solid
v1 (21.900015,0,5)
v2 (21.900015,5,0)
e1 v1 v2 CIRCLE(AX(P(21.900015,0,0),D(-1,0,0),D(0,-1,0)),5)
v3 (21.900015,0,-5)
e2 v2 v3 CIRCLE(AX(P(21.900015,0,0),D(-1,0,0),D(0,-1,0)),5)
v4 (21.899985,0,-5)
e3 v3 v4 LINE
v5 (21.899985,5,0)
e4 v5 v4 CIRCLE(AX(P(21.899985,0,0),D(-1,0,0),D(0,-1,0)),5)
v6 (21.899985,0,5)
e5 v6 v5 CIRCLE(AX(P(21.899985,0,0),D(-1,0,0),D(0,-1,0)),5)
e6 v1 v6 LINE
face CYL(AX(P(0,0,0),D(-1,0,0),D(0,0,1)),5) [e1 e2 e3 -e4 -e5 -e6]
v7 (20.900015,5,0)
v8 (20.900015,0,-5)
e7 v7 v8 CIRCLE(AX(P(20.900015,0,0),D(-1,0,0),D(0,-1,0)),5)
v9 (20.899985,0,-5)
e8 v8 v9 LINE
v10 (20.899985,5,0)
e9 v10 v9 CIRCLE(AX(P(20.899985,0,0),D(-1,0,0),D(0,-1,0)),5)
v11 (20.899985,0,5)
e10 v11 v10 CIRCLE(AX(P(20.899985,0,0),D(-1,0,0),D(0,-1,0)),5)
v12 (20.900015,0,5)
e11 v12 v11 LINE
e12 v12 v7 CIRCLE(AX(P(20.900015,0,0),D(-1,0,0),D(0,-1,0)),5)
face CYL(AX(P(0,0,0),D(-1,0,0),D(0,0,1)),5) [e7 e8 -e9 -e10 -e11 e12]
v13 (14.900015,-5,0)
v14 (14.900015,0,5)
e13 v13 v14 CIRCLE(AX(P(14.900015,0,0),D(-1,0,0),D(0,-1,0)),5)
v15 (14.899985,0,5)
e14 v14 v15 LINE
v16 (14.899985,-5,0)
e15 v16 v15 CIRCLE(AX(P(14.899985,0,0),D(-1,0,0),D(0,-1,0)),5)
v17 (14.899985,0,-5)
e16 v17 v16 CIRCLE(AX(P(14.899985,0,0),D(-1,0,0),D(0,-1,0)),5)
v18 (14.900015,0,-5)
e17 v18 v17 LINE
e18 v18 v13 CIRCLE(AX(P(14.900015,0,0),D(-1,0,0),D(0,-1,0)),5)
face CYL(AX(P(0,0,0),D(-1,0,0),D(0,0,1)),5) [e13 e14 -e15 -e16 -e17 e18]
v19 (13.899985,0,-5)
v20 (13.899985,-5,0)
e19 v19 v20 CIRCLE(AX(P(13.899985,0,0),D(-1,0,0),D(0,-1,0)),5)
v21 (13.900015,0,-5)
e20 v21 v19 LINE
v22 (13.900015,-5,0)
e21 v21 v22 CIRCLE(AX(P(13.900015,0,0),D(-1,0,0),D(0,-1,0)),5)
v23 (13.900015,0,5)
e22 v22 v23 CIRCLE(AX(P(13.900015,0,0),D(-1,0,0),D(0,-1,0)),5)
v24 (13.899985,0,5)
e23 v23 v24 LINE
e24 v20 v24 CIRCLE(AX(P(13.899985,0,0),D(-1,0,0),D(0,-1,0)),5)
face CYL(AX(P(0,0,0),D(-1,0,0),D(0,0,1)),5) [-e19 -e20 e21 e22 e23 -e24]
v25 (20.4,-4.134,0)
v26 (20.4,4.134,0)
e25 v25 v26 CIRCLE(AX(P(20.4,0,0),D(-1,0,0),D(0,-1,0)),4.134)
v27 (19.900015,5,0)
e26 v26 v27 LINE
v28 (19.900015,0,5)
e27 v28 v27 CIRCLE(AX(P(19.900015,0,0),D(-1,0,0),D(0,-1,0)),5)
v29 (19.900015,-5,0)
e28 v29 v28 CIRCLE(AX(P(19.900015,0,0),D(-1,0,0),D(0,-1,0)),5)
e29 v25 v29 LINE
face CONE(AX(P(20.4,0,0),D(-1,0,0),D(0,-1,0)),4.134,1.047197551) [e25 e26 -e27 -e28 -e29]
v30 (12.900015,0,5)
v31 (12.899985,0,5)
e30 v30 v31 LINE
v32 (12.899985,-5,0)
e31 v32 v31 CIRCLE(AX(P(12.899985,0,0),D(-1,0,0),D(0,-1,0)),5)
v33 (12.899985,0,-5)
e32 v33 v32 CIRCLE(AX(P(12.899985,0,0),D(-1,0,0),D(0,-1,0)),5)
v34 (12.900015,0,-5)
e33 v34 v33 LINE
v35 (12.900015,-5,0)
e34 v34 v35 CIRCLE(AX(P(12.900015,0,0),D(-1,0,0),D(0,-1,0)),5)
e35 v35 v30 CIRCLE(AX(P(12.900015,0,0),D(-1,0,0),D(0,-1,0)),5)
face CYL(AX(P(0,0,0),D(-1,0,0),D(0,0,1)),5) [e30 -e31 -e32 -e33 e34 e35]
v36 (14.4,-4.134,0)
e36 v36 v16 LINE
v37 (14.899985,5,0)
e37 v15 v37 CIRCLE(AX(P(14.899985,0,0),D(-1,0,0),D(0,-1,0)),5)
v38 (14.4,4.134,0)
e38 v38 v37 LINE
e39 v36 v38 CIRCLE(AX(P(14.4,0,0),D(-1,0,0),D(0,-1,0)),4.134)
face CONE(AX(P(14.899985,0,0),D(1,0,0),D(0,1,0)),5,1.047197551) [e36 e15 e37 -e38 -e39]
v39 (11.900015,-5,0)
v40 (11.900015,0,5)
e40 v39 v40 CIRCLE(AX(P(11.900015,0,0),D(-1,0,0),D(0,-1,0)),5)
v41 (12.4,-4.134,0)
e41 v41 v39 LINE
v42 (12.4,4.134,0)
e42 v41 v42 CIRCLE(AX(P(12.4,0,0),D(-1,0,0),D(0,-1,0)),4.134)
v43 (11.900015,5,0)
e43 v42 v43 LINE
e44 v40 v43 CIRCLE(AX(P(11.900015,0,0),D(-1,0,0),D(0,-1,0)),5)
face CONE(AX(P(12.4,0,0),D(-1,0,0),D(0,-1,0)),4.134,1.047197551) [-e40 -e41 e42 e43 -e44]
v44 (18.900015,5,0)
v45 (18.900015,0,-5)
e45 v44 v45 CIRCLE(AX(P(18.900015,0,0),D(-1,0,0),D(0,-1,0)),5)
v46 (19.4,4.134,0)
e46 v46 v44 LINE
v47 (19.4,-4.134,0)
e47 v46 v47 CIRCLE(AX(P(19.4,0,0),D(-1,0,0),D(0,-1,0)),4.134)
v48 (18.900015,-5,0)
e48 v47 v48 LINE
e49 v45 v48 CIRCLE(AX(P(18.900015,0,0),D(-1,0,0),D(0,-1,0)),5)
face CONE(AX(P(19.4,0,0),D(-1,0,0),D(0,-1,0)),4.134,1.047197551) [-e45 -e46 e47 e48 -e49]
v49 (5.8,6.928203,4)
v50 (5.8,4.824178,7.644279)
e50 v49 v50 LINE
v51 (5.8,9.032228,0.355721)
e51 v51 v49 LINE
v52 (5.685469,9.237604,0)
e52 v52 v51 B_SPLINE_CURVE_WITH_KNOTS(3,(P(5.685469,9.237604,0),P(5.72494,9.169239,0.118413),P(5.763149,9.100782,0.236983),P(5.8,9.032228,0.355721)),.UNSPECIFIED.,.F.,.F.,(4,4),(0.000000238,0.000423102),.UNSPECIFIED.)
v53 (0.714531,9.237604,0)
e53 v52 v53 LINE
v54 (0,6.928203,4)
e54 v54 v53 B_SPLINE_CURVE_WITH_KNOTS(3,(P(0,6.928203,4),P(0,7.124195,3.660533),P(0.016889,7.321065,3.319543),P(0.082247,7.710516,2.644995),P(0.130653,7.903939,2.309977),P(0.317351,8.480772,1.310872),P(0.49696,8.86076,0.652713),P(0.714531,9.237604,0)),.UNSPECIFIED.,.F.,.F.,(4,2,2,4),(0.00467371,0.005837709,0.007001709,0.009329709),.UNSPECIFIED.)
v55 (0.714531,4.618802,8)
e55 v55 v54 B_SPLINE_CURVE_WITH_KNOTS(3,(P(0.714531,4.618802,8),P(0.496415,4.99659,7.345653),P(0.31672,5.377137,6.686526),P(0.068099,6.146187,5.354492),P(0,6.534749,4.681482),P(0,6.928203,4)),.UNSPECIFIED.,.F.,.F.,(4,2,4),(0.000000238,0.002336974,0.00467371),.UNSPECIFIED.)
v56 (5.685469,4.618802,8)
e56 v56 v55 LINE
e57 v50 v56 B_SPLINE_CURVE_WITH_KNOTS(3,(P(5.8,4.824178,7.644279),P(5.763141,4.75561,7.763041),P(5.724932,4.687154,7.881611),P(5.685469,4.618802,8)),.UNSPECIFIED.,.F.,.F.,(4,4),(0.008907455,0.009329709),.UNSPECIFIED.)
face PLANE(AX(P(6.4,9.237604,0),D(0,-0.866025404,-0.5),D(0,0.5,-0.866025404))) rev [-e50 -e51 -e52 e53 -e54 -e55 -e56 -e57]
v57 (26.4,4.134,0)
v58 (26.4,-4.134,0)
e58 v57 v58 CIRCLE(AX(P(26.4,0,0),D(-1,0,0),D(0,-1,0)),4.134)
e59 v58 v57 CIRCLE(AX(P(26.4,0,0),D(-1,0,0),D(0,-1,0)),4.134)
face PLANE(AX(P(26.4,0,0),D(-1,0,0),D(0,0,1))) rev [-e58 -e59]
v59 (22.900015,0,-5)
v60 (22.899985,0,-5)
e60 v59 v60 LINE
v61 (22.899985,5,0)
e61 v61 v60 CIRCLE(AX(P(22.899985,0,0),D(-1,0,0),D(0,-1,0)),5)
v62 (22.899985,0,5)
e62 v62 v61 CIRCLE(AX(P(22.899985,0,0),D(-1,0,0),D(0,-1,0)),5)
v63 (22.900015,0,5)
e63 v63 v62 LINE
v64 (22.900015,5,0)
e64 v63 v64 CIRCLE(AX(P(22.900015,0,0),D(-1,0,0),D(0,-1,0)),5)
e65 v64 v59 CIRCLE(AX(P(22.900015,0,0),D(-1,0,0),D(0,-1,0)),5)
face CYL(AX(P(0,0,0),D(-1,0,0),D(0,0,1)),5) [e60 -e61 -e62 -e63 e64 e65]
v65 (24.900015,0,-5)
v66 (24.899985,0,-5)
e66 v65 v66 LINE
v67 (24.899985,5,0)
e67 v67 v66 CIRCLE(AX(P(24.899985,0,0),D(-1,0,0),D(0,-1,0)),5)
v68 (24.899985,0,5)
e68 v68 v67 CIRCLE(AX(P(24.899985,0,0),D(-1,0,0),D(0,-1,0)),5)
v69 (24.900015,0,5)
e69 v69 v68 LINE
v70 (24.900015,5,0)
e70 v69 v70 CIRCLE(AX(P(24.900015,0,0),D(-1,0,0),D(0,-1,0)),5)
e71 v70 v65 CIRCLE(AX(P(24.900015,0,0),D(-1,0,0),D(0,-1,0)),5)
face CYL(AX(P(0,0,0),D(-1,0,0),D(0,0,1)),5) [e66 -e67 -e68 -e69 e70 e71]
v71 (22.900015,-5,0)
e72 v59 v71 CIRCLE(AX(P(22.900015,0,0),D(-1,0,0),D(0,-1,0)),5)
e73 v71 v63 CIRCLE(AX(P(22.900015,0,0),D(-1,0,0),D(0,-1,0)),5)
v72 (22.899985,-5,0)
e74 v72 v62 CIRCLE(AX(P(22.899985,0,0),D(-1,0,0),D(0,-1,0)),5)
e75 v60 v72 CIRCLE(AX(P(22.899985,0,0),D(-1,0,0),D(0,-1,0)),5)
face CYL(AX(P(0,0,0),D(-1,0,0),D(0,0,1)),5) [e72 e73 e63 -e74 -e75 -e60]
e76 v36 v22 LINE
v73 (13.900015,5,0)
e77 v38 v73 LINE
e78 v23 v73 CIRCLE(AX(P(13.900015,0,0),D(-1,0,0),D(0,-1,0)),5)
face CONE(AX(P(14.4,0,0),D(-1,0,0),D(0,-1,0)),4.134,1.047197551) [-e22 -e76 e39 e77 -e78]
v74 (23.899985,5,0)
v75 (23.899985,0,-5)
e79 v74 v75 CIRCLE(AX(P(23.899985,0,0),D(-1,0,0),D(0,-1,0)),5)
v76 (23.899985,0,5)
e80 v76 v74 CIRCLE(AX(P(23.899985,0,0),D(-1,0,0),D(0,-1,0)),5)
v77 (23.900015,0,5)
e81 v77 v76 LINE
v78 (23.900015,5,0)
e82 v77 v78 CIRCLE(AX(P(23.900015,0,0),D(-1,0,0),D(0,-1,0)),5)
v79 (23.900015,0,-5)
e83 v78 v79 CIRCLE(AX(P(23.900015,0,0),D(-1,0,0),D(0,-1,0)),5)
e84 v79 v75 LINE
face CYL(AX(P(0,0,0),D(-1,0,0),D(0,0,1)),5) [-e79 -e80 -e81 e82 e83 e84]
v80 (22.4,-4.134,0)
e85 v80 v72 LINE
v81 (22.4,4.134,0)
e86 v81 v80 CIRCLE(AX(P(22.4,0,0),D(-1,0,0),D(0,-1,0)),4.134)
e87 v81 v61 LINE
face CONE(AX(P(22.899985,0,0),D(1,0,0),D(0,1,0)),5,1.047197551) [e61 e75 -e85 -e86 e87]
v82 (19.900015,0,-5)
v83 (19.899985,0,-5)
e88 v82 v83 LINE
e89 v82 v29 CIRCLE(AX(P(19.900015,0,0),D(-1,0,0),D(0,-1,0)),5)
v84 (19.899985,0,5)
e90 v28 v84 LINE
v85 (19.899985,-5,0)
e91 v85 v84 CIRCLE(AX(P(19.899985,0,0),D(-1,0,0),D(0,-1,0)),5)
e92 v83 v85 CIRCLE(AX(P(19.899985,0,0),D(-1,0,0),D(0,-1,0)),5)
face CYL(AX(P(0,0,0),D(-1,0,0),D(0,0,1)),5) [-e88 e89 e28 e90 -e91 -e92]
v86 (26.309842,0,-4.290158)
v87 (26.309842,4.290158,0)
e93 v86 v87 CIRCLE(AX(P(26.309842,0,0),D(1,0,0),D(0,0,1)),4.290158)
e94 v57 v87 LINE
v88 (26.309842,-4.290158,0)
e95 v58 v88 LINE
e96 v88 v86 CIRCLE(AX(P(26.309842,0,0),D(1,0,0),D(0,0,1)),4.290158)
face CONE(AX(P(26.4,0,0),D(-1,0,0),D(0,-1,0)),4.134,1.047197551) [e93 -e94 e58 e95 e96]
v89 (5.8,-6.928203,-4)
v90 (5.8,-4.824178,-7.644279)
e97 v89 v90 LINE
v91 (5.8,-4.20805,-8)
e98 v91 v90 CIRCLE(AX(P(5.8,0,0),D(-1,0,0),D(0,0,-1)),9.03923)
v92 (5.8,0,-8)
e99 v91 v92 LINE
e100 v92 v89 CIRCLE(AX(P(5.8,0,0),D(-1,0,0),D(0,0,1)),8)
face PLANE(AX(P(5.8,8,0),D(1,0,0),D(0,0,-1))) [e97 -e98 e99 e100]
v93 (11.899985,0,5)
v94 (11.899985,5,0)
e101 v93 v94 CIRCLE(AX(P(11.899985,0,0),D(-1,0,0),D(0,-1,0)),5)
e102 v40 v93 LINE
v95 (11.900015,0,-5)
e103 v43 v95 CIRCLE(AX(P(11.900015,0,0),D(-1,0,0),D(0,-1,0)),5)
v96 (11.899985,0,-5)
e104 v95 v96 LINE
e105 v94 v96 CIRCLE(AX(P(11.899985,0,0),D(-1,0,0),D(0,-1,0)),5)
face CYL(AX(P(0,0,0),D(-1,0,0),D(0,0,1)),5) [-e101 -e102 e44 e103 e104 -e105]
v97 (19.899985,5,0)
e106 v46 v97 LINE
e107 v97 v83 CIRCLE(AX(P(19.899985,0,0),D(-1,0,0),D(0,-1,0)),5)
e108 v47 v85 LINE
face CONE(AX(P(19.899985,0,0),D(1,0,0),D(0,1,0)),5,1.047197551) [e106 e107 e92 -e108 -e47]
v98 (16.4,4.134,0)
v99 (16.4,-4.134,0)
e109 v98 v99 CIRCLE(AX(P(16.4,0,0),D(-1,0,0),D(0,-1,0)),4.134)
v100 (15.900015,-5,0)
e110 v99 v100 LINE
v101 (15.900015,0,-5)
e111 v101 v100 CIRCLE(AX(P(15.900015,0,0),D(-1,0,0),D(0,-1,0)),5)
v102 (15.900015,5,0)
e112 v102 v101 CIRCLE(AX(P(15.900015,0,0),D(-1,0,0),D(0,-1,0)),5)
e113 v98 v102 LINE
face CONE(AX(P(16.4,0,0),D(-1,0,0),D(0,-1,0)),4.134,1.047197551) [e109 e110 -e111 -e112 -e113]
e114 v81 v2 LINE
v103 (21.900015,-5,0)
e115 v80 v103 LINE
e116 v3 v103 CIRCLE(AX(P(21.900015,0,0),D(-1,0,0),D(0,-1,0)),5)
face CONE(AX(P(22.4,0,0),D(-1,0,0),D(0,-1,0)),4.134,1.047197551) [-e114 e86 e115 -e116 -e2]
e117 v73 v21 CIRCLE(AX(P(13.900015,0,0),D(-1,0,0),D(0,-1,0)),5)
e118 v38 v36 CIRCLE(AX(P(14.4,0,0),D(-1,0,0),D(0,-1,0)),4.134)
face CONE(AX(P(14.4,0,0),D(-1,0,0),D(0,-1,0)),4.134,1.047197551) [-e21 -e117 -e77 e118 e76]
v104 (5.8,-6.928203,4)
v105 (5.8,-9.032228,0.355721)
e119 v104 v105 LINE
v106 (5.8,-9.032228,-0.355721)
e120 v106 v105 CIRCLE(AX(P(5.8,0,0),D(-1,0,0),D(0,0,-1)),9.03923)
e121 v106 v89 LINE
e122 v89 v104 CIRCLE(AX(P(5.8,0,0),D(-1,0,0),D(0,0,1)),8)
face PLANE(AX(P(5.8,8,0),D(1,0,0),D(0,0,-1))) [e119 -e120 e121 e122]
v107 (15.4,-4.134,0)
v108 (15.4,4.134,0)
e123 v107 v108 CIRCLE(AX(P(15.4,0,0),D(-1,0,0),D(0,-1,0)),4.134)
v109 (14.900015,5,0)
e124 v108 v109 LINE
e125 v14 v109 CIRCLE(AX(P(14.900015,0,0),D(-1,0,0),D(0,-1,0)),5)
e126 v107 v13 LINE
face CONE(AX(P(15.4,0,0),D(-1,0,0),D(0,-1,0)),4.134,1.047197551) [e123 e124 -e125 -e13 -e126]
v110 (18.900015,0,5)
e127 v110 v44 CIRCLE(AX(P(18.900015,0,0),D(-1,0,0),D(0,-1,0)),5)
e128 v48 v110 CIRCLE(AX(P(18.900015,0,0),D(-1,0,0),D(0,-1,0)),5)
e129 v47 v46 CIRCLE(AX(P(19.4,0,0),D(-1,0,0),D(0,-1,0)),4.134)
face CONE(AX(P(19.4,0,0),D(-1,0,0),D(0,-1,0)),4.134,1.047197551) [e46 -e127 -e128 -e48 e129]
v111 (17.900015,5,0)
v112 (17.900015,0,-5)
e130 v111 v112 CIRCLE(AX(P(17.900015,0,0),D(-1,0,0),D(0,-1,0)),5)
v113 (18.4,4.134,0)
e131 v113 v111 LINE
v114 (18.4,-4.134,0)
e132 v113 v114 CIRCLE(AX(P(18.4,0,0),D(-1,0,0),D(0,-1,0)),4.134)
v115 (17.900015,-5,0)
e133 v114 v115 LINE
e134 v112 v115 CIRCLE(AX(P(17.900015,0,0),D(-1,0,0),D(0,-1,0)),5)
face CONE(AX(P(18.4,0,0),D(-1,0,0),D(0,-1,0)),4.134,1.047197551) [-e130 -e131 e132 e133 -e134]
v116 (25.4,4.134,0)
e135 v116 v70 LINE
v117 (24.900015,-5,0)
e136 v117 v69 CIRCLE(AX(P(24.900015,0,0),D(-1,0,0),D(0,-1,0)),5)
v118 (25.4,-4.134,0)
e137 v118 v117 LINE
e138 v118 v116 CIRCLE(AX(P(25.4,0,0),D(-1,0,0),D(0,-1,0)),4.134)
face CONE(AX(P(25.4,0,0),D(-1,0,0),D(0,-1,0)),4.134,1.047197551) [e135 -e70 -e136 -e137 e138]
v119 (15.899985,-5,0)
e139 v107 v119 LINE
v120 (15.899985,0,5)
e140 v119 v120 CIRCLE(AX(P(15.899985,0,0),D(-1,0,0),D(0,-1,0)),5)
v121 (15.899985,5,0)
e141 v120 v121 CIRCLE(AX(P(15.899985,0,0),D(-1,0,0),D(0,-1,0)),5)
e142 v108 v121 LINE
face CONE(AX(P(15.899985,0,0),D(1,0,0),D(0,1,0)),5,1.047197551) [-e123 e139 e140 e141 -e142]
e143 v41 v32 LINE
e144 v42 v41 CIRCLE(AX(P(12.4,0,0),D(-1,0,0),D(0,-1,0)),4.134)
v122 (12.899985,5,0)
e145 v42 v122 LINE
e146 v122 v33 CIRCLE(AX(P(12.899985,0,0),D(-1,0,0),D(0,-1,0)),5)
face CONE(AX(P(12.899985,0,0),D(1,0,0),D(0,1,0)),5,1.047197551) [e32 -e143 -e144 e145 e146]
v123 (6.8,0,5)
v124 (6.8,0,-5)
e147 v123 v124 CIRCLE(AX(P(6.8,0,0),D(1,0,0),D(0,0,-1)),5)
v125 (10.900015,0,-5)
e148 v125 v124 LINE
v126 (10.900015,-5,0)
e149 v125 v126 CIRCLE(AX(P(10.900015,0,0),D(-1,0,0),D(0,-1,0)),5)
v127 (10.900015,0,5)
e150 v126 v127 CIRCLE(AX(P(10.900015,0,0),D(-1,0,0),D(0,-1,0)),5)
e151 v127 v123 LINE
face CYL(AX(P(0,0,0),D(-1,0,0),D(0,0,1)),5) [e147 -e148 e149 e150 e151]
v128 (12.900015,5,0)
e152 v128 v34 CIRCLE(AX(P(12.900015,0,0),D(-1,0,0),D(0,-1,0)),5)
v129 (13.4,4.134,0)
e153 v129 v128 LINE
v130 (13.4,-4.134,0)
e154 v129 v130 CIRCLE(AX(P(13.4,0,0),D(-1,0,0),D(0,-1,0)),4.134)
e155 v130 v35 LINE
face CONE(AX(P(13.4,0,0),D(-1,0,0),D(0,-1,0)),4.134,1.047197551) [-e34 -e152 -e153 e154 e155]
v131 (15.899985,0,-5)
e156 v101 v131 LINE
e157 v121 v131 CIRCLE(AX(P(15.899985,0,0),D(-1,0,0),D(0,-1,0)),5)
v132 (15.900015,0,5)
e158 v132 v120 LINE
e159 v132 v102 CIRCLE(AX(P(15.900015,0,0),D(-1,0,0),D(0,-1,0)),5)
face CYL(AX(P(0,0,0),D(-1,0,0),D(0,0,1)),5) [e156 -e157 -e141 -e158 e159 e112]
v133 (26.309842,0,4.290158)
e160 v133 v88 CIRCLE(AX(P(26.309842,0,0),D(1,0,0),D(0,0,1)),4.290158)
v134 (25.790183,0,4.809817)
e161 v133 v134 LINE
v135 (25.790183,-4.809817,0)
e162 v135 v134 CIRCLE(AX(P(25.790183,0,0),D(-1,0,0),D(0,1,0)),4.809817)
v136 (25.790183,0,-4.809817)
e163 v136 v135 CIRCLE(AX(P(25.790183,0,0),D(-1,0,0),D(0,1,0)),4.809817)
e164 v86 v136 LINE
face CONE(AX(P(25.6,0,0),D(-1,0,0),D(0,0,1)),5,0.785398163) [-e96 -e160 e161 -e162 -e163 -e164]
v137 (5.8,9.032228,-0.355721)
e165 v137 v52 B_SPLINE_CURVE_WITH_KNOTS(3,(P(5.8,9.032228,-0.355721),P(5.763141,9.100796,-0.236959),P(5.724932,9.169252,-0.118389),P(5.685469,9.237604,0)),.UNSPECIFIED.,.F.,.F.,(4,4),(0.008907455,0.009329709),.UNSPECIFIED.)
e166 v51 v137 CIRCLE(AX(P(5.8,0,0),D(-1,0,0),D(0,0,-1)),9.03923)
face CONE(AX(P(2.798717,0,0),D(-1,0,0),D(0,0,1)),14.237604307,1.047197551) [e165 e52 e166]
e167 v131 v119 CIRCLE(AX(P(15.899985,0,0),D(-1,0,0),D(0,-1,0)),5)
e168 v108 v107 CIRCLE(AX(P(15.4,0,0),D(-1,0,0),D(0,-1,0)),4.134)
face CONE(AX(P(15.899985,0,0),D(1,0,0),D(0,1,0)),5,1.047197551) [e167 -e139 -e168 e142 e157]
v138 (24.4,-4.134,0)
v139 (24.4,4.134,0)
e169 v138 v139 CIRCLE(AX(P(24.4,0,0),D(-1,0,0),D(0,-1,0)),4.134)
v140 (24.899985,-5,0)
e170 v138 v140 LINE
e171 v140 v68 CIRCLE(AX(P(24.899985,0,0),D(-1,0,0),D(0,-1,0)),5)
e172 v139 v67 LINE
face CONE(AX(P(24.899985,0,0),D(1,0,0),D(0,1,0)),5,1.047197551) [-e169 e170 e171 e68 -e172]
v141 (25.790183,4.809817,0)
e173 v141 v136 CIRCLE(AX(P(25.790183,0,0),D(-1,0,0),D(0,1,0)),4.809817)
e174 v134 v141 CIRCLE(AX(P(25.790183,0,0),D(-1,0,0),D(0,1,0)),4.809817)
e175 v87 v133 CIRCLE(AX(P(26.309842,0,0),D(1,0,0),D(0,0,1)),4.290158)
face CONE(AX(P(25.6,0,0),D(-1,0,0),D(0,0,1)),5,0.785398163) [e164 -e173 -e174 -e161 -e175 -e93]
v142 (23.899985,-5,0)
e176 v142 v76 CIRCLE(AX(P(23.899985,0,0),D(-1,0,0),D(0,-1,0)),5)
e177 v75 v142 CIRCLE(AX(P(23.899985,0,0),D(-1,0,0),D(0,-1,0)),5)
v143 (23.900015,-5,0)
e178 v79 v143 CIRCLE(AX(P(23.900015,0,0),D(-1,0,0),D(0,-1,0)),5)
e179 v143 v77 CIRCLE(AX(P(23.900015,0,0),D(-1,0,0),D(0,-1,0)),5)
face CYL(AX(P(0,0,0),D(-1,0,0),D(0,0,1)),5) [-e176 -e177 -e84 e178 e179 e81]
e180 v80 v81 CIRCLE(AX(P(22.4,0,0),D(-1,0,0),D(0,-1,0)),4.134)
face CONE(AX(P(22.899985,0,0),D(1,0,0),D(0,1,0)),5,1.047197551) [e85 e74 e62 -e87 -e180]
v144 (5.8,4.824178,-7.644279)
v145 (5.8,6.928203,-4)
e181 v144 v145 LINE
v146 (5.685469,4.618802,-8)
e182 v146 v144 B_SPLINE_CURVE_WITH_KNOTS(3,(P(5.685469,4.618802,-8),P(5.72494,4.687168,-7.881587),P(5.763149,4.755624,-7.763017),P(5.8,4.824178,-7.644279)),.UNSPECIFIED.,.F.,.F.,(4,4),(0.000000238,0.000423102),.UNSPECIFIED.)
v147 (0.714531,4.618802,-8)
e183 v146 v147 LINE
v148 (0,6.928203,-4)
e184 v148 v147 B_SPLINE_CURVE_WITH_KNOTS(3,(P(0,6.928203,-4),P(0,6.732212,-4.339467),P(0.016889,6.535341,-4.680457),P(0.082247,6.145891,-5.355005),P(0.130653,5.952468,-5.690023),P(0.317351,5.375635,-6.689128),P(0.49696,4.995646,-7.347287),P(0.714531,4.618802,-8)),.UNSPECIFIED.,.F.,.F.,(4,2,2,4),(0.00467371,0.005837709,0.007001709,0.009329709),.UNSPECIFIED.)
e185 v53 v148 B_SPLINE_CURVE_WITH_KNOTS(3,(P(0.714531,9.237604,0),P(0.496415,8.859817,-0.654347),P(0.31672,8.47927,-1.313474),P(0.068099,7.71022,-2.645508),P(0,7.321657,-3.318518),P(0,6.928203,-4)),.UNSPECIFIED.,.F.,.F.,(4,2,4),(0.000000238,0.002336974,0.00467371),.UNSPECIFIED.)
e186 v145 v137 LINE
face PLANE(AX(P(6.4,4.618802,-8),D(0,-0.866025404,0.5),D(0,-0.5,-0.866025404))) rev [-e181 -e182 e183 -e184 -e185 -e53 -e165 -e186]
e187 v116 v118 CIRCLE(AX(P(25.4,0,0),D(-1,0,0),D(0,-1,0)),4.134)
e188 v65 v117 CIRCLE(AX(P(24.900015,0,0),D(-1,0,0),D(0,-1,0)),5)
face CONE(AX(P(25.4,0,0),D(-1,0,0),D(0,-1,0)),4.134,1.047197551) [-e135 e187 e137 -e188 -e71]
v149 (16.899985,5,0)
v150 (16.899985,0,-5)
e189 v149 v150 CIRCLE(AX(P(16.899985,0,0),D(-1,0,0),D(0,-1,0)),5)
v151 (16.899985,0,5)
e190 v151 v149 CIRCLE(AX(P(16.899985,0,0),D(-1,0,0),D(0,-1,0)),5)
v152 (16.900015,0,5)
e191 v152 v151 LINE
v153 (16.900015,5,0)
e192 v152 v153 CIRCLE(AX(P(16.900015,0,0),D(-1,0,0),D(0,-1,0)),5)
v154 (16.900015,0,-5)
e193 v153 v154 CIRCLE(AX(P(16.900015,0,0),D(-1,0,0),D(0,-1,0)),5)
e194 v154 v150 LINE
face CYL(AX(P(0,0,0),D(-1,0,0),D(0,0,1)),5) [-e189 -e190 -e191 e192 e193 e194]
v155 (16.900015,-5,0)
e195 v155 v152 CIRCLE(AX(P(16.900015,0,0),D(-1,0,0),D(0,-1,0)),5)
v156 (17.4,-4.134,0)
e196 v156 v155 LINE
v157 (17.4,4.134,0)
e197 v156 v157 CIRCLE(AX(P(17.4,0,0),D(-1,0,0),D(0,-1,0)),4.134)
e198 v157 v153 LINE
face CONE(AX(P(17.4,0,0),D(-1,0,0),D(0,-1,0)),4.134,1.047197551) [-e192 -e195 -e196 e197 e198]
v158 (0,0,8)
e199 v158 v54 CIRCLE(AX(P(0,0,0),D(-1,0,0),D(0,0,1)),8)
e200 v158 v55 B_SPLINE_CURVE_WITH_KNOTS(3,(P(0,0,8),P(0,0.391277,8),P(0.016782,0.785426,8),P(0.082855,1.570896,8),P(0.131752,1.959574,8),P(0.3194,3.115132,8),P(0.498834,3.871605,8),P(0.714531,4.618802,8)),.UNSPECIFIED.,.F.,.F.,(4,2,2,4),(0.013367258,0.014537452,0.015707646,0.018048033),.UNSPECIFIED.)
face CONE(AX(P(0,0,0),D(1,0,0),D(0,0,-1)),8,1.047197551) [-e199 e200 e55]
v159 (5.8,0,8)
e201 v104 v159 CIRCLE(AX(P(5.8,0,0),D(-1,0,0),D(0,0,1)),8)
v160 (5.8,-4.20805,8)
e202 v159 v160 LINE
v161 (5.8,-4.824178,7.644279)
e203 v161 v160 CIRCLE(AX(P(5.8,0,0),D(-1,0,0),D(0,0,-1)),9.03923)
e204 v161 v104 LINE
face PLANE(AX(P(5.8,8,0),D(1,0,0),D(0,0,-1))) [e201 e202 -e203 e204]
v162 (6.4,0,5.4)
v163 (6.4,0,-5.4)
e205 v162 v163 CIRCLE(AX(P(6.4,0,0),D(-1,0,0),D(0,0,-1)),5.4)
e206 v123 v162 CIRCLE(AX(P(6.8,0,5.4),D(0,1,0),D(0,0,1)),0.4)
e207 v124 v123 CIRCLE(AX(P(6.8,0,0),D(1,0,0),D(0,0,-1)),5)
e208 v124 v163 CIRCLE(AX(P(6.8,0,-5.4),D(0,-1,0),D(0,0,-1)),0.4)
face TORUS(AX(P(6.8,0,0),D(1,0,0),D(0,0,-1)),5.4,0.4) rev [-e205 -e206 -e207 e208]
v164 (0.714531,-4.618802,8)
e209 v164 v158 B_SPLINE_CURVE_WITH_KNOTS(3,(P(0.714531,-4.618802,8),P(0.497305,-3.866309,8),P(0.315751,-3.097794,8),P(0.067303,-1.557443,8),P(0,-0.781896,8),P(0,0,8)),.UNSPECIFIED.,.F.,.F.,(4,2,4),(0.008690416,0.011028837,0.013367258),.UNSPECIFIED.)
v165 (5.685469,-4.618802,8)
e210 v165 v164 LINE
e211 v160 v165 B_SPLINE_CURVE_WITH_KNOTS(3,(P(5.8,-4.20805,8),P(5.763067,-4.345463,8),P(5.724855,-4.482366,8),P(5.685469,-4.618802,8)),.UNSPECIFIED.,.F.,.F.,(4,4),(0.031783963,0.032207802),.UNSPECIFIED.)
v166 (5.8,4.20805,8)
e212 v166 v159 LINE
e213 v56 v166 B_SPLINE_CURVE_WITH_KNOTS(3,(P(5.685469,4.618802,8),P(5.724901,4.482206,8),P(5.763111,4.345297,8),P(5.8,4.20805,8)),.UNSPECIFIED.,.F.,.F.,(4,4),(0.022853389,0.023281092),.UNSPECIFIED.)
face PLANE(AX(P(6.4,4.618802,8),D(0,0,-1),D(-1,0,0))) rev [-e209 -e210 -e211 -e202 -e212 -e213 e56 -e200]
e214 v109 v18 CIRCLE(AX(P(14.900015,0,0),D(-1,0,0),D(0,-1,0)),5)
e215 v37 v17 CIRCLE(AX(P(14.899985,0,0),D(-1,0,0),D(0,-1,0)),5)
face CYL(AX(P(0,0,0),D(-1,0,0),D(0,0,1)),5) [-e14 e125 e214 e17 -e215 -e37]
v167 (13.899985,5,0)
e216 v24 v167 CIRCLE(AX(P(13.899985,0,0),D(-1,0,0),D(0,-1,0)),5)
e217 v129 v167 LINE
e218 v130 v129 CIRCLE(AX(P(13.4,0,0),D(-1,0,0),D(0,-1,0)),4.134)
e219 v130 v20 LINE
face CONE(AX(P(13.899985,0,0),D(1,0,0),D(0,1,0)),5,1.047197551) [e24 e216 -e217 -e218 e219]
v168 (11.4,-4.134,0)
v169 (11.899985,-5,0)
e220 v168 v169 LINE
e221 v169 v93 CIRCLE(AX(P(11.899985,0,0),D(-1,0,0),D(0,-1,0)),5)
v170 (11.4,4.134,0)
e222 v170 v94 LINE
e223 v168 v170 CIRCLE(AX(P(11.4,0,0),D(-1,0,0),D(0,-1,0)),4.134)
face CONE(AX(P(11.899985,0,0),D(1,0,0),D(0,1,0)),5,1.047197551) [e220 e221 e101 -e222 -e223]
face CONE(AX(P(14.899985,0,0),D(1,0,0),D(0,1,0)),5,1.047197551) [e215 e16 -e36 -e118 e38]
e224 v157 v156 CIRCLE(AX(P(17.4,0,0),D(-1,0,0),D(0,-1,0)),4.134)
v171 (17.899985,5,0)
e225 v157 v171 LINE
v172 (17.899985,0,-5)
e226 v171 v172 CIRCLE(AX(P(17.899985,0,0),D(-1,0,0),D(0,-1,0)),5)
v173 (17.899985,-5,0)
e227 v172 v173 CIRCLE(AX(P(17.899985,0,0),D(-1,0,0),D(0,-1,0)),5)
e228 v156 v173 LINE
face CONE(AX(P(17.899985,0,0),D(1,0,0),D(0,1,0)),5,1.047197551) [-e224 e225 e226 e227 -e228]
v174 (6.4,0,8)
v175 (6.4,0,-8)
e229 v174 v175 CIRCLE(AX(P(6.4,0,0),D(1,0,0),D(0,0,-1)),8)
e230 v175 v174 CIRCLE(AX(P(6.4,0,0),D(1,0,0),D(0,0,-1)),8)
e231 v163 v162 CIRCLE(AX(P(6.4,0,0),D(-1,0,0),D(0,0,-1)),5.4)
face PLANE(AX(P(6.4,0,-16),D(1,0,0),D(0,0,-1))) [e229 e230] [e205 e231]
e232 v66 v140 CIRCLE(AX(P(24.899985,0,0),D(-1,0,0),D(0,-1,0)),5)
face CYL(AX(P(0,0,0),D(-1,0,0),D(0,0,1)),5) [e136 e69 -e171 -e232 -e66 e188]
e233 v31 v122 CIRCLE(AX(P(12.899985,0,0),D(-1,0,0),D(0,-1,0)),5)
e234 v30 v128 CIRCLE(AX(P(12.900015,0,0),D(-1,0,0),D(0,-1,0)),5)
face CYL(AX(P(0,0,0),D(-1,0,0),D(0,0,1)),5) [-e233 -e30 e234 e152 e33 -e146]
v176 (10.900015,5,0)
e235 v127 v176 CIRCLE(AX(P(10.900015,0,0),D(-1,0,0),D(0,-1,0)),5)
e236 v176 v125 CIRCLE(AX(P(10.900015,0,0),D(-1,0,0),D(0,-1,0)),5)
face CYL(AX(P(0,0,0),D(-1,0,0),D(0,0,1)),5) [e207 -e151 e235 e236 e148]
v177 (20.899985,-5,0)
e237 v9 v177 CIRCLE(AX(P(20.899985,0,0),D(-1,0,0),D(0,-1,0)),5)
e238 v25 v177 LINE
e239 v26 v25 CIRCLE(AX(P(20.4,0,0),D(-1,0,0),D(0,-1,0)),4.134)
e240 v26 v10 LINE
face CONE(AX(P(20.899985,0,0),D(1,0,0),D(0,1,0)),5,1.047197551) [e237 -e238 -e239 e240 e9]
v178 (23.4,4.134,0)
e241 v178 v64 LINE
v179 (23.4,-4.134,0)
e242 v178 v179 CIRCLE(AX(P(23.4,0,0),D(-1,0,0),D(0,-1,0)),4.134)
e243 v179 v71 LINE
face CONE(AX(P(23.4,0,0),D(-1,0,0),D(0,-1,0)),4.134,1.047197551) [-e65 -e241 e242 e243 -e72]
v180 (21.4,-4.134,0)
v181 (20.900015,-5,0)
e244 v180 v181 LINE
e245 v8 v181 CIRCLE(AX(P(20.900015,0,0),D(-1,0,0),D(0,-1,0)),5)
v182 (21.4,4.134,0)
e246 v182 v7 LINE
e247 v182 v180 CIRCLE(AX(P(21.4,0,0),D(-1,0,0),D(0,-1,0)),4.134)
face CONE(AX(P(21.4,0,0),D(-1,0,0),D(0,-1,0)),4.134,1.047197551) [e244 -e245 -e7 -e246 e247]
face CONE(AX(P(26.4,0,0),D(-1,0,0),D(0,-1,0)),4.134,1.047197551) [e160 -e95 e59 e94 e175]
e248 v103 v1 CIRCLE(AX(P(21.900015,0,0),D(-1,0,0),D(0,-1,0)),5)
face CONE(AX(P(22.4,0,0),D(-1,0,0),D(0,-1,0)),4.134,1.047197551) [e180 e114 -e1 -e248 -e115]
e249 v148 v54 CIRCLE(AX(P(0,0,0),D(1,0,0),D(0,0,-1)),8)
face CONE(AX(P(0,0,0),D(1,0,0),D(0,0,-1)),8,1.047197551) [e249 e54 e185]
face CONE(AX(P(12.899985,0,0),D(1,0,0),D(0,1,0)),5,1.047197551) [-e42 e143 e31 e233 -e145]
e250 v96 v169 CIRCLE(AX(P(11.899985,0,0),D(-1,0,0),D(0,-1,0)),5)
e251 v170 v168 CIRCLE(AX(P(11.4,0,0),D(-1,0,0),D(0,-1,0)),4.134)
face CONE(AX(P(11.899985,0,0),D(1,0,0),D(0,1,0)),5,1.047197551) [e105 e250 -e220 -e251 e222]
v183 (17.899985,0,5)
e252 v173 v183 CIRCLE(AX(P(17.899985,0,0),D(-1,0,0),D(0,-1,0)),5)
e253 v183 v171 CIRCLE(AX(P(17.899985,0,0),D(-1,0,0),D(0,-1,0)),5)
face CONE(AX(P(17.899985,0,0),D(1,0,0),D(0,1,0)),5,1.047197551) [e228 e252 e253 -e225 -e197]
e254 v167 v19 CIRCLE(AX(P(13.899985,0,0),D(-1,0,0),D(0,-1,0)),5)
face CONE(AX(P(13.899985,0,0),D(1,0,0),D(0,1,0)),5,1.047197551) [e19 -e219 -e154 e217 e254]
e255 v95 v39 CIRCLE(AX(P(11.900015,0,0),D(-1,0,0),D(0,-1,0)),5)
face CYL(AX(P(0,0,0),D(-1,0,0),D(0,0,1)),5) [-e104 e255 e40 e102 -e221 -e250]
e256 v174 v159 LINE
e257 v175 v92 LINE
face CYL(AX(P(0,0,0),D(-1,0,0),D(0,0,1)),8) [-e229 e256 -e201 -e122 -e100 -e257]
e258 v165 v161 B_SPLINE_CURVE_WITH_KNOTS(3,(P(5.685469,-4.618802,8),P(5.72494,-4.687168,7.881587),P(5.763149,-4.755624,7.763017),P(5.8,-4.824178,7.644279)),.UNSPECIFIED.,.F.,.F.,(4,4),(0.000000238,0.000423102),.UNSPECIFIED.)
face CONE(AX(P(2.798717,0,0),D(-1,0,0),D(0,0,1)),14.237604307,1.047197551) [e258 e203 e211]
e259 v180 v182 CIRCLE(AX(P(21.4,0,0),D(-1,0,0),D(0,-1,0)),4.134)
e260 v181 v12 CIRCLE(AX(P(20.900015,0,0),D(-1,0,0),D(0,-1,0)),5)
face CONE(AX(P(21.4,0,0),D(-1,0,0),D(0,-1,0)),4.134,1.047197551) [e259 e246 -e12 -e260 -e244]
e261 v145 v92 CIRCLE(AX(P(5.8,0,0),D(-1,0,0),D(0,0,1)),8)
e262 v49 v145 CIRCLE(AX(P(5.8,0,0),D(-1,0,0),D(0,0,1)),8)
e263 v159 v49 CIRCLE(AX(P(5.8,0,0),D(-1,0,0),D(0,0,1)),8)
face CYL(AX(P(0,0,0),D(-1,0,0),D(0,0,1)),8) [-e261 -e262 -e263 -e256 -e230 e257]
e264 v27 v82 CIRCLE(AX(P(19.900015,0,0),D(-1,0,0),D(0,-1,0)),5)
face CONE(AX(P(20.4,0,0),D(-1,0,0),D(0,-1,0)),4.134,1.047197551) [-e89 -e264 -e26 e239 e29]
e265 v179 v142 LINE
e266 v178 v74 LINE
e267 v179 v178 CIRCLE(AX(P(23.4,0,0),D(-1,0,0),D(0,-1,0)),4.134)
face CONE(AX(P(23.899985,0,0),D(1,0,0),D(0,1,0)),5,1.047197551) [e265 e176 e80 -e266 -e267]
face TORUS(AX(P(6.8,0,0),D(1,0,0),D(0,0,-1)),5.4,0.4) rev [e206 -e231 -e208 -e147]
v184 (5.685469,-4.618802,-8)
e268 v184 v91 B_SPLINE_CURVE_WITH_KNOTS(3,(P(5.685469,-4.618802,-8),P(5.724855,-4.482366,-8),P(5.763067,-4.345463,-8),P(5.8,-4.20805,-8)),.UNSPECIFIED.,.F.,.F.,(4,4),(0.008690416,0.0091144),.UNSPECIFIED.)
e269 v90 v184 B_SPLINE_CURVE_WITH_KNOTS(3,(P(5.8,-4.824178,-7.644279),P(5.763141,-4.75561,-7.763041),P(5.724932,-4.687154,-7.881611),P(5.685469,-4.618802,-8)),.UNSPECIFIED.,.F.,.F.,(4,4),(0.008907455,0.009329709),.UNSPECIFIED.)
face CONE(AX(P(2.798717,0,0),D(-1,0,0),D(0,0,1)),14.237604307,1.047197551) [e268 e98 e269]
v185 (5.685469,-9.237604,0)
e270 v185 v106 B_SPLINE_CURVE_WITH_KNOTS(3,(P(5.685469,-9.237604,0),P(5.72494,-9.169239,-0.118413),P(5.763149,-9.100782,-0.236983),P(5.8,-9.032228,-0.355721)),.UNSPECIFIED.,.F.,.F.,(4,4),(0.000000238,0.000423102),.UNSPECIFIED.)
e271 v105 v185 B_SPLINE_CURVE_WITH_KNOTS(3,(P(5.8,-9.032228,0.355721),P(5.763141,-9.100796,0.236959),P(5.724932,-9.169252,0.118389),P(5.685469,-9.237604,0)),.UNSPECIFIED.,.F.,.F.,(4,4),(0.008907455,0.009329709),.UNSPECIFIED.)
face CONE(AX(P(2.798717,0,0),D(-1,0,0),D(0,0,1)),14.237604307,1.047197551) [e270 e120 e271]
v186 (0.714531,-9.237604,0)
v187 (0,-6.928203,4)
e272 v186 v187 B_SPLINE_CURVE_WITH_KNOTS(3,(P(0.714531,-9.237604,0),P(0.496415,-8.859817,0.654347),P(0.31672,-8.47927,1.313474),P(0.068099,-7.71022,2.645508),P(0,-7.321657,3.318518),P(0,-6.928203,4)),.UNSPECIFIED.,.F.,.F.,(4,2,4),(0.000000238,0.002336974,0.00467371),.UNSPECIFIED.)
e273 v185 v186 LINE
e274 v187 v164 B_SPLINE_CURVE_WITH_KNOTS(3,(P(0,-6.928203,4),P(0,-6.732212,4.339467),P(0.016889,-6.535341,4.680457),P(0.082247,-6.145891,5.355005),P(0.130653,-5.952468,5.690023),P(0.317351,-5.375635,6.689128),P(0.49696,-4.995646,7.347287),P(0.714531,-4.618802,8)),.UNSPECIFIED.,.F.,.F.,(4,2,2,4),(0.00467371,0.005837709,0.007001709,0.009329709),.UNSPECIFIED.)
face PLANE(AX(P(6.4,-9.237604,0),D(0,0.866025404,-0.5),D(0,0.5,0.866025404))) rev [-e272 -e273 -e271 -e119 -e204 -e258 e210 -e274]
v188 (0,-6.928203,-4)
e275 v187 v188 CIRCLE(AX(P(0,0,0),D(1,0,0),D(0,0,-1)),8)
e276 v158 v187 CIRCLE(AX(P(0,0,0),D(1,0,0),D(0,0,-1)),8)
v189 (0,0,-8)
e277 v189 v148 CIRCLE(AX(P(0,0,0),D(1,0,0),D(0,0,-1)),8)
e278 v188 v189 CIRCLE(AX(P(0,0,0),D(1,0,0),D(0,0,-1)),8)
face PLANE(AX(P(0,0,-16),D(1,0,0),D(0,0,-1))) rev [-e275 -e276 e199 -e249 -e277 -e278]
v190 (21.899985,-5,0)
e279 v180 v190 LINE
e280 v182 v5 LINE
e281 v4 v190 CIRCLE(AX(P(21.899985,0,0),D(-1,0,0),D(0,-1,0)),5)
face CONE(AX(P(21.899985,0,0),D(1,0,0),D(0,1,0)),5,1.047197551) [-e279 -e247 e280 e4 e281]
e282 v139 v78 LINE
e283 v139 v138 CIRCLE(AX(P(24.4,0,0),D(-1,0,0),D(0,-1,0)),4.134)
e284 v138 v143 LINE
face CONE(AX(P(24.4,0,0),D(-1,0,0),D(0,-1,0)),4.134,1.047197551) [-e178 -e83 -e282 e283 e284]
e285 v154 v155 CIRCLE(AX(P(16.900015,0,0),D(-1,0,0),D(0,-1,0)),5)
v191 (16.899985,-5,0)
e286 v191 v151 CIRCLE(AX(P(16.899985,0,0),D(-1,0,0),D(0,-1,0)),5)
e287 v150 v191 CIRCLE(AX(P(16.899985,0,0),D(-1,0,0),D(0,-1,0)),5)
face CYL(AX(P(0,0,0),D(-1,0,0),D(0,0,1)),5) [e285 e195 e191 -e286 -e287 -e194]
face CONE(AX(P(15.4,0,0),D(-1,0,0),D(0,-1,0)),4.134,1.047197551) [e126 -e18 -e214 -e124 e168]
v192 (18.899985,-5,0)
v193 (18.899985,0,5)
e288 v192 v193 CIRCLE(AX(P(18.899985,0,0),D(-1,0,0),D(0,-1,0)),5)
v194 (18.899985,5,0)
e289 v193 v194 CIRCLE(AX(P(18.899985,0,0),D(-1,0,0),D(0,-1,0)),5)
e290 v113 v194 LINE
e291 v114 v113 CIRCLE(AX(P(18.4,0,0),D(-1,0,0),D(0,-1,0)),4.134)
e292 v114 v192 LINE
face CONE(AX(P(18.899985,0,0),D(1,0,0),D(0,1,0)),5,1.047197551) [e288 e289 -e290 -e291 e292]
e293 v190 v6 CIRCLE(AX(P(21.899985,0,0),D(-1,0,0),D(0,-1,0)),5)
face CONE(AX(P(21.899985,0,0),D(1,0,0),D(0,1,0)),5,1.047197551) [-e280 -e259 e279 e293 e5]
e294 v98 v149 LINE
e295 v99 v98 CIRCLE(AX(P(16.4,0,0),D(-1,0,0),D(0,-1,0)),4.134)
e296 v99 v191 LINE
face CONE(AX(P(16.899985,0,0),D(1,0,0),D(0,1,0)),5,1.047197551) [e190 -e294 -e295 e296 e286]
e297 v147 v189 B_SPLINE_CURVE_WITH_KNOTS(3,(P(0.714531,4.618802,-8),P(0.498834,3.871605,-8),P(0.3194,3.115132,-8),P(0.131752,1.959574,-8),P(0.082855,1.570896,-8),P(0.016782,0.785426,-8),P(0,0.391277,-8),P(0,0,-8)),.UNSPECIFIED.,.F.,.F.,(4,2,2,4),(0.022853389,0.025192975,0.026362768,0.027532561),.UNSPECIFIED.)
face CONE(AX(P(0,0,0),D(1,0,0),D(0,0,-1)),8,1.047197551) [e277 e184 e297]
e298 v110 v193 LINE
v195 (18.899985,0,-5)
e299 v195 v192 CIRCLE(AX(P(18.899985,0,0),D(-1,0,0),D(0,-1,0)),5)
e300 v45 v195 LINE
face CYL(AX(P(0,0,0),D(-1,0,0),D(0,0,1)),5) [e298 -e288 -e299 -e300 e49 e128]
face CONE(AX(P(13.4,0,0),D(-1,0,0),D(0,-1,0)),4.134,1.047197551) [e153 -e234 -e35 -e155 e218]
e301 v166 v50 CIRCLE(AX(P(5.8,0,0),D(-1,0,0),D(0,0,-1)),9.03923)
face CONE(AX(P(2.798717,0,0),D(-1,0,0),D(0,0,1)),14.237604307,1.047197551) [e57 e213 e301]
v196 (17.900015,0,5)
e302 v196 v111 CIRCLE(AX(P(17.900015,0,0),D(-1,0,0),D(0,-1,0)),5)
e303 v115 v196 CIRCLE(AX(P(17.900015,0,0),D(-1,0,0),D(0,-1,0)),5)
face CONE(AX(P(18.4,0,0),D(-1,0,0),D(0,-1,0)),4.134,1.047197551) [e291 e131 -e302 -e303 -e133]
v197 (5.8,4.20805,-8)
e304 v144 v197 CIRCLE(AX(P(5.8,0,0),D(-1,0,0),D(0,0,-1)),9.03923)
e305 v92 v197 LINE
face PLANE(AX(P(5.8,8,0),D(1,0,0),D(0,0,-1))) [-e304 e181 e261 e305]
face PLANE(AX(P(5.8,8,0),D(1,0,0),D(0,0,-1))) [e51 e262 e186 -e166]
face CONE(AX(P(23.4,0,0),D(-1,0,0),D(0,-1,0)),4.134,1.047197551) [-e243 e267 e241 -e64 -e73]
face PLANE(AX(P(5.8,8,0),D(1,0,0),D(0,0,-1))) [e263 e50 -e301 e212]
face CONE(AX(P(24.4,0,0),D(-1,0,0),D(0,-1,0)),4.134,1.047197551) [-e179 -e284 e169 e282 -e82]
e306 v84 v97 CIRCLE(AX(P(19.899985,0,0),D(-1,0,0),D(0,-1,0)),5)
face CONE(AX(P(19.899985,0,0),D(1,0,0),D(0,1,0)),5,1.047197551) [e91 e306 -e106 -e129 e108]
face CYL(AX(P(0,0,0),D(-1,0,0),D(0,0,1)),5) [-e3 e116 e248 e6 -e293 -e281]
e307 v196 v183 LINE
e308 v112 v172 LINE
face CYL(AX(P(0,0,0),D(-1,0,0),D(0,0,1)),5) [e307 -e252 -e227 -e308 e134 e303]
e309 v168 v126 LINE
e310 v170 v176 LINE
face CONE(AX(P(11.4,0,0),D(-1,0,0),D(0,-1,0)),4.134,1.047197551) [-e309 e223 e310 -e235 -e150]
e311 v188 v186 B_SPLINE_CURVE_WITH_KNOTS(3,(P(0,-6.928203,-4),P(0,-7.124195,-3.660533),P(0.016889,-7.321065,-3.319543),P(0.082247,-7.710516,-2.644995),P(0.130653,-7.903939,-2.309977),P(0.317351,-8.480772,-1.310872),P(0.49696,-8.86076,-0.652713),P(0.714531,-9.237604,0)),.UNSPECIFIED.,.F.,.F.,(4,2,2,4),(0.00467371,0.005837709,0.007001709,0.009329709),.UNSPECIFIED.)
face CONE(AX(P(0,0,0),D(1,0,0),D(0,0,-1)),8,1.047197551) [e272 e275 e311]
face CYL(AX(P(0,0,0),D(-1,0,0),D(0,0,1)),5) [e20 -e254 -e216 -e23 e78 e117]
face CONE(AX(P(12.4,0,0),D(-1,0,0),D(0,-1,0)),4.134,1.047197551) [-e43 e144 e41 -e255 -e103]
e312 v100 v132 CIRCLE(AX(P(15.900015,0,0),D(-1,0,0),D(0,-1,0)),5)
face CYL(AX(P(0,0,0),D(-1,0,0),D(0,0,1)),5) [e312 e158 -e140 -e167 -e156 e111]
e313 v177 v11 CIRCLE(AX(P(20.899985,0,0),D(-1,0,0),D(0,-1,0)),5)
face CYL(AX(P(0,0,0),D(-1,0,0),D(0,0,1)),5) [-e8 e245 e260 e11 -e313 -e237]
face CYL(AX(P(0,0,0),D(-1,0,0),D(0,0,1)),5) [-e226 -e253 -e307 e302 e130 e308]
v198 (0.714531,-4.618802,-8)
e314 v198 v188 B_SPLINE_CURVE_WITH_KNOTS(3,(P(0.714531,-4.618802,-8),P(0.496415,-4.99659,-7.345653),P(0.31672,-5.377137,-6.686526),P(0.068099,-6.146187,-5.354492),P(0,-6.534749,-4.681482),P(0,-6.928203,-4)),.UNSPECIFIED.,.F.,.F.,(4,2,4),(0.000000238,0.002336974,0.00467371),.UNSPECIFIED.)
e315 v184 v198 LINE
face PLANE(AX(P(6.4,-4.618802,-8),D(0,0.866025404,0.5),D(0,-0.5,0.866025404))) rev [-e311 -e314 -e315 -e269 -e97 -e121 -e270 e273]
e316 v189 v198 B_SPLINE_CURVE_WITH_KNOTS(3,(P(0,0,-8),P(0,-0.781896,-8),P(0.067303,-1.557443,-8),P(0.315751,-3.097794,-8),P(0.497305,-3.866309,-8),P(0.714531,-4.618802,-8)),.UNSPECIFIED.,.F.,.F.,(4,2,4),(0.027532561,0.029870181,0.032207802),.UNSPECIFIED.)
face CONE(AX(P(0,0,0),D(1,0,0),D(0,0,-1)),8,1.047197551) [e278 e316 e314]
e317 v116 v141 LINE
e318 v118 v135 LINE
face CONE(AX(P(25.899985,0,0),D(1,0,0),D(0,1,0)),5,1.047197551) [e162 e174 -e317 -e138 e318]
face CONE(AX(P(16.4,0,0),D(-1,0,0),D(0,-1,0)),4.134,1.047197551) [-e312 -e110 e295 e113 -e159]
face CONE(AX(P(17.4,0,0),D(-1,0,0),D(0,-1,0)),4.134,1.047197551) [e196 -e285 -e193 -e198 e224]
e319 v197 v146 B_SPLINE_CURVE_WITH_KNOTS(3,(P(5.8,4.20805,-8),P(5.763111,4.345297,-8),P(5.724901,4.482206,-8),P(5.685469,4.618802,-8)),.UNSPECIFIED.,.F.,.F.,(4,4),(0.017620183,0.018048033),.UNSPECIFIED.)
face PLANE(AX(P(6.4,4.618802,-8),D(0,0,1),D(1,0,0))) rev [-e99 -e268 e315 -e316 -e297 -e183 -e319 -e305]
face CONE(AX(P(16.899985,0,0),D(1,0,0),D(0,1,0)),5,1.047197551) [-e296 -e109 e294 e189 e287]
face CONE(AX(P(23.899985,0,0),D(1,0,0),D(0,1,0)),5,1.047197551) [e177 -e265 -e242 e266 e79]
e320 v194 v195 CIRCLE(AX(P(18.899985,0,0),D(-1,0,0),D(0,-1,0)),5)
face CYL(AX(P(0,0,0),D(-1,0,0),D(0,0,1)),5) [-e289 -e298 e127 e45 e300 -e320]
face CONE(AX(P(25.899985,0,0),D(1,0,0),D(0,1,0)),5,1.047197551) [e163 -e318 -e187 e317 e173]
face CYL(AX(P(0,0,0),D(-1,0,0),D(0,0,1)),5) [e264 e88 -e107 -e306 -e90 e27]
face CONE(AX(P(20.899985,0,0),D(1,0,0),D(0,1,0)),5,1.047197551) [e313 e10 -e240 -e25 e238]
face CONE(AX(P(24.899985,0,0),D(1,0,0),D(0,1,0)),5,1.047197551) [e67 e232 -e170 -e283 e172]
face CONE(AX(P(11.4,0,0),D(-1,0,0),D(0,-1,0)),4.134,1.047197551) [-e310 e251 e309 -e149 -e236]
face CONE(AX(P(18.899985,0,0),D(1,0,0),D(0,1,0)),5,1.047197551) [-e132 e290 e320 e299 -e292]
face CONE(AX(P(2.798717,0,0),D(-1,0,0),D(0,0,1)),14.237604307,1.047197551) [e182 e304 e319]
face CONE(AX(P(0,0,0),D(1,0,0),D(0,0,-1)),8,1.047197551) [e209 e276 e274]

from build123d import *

# Parameters (mm, degrees)
EXTRUDE_393_DEPTH      = 6.4
SKETCH_4_W             = 0.6
SKETCH_4_H             = 11.237604307
CHAMFER_2074_SIZE      = 0.8
FILLET_2119_R          = 0.4
PATTERN_LINEAR_1_COUNT = 16
PATTERN_LINEAR_1_PITCH = 1


with BuildPart() as part:
    # 草图1 → Extrude 393 (new body)
    with BuildSketch(Plane(origin=(0, 0, 0), x_dir=(0, 0, -1), z_dir=(1, 0, 0))):
        Polygon((8, 4.618802154), (8, -4.618802154), (0, -9.237604307), (-8, -4.618802154), (-8, 4.618802154), (0, 9.237604307), align=None)
    extrude(amount=EXTRUDE_393_DEPTH)

    # 草图2 → 凸台-旋转1 (revolve)
    with BuildSketch(Plane.XY, mode=Mode.PRIVATE) as revolve_1_sk:
        Polygon((0, 0), (26.4, 0), (26.4, 4.134), (26.4, 5), (0, 5), align=None)
    revolve(revolve_1_sk.sketch.rotate(Axis((0, 0, 0), (1, 0, 0)), 90), axis=Axis((0, 0, 0), (1, 0, 0)))

    # 草图3 → 切除-旋转1 (revolve, cut)
    with BuildSketch(Plane.XY):
        Polygon((0, 8), (3.601282526, 14.237604307), (3.601282526, 19.237604307), (-10, 19.237604307), (-10, 8), align=None)
    revolve(axis=Axis((0, 0, 0), (1, 0, 0)), mode=Mode.SUBTRACT)

    # 草图5 → 切除-旋转2 (revolve, cut)
    with BuildSketch(Plane.XY):
        Polygon((6.4, 8), (2.798717474, 14.237604307), (2.798717474, 19.237604307), (12.798717474, 19.237604307), (12.798717474, 8), align=None)
    revolve(axis=Axis((0, 0, 0), (1, 0, 0)), mode=Mode.SUBTRACT)

    # 草图4 → 切除-旋转3 (revolve, cut)
    with BuildSketch(Plane.XY, mode=Mode.PRIVATE) as cut_revolve_3_sk:
        with Locations((6.1, 13.618802154)):
            Rectangle(SKETCH_4_W, SKETCH_4_H)
    revolve(cut_revolve_3_sk.sketch.rotate(Axis((0, 0, 0), (1, 0, 0)), 270), axis=Axis((0, 0, 0), (1, 0, 0)), mode=Mode.SUBTRACT)

    # Chamfer 2074
    chamfer_2074_edges = [part.edges().sort_by_distance(p)[0] for p in [
        (26.4, 0, -5),
    ]]
    chamfer(chamfer_2074_edges, length=CHAMFER_2074_SIZE)

    # Fillet 2119
    fillet_2119_edges = [part.edges().sort_by_distance(p)[0] for p in [
        (6.4, 0, -5),
    ]]
    fillet(fillet_2119_edges, radius=FILLET_2119_R)

    # 草图6 → 切除-旋转4 (revolve, cut)
    with BuildSketch(Plane.XY):
        Polygon((11.4, -4.134), (10.900014667, -5), (10.900014667, -6.25), (11.899985333, -6.25), (11.899985333, -5), align=None)
    cut_revolve_4 = revolve(axis=Axis((-3.175, 0, 0), (1, 0, 0)), mode=Mode.SUBTRACT)

    # 阵列(线性)1: 切除-旋转4 ×16
    with Locations(*[(i * PATTERN_LINEAR_1_PITCH, 0, 0) for i in range(1, PATTERN_LINEAR_1_COUNT)]):
        add(cut_revolve_4, mode=Mode.SUBTRACT)


solid = part.part
